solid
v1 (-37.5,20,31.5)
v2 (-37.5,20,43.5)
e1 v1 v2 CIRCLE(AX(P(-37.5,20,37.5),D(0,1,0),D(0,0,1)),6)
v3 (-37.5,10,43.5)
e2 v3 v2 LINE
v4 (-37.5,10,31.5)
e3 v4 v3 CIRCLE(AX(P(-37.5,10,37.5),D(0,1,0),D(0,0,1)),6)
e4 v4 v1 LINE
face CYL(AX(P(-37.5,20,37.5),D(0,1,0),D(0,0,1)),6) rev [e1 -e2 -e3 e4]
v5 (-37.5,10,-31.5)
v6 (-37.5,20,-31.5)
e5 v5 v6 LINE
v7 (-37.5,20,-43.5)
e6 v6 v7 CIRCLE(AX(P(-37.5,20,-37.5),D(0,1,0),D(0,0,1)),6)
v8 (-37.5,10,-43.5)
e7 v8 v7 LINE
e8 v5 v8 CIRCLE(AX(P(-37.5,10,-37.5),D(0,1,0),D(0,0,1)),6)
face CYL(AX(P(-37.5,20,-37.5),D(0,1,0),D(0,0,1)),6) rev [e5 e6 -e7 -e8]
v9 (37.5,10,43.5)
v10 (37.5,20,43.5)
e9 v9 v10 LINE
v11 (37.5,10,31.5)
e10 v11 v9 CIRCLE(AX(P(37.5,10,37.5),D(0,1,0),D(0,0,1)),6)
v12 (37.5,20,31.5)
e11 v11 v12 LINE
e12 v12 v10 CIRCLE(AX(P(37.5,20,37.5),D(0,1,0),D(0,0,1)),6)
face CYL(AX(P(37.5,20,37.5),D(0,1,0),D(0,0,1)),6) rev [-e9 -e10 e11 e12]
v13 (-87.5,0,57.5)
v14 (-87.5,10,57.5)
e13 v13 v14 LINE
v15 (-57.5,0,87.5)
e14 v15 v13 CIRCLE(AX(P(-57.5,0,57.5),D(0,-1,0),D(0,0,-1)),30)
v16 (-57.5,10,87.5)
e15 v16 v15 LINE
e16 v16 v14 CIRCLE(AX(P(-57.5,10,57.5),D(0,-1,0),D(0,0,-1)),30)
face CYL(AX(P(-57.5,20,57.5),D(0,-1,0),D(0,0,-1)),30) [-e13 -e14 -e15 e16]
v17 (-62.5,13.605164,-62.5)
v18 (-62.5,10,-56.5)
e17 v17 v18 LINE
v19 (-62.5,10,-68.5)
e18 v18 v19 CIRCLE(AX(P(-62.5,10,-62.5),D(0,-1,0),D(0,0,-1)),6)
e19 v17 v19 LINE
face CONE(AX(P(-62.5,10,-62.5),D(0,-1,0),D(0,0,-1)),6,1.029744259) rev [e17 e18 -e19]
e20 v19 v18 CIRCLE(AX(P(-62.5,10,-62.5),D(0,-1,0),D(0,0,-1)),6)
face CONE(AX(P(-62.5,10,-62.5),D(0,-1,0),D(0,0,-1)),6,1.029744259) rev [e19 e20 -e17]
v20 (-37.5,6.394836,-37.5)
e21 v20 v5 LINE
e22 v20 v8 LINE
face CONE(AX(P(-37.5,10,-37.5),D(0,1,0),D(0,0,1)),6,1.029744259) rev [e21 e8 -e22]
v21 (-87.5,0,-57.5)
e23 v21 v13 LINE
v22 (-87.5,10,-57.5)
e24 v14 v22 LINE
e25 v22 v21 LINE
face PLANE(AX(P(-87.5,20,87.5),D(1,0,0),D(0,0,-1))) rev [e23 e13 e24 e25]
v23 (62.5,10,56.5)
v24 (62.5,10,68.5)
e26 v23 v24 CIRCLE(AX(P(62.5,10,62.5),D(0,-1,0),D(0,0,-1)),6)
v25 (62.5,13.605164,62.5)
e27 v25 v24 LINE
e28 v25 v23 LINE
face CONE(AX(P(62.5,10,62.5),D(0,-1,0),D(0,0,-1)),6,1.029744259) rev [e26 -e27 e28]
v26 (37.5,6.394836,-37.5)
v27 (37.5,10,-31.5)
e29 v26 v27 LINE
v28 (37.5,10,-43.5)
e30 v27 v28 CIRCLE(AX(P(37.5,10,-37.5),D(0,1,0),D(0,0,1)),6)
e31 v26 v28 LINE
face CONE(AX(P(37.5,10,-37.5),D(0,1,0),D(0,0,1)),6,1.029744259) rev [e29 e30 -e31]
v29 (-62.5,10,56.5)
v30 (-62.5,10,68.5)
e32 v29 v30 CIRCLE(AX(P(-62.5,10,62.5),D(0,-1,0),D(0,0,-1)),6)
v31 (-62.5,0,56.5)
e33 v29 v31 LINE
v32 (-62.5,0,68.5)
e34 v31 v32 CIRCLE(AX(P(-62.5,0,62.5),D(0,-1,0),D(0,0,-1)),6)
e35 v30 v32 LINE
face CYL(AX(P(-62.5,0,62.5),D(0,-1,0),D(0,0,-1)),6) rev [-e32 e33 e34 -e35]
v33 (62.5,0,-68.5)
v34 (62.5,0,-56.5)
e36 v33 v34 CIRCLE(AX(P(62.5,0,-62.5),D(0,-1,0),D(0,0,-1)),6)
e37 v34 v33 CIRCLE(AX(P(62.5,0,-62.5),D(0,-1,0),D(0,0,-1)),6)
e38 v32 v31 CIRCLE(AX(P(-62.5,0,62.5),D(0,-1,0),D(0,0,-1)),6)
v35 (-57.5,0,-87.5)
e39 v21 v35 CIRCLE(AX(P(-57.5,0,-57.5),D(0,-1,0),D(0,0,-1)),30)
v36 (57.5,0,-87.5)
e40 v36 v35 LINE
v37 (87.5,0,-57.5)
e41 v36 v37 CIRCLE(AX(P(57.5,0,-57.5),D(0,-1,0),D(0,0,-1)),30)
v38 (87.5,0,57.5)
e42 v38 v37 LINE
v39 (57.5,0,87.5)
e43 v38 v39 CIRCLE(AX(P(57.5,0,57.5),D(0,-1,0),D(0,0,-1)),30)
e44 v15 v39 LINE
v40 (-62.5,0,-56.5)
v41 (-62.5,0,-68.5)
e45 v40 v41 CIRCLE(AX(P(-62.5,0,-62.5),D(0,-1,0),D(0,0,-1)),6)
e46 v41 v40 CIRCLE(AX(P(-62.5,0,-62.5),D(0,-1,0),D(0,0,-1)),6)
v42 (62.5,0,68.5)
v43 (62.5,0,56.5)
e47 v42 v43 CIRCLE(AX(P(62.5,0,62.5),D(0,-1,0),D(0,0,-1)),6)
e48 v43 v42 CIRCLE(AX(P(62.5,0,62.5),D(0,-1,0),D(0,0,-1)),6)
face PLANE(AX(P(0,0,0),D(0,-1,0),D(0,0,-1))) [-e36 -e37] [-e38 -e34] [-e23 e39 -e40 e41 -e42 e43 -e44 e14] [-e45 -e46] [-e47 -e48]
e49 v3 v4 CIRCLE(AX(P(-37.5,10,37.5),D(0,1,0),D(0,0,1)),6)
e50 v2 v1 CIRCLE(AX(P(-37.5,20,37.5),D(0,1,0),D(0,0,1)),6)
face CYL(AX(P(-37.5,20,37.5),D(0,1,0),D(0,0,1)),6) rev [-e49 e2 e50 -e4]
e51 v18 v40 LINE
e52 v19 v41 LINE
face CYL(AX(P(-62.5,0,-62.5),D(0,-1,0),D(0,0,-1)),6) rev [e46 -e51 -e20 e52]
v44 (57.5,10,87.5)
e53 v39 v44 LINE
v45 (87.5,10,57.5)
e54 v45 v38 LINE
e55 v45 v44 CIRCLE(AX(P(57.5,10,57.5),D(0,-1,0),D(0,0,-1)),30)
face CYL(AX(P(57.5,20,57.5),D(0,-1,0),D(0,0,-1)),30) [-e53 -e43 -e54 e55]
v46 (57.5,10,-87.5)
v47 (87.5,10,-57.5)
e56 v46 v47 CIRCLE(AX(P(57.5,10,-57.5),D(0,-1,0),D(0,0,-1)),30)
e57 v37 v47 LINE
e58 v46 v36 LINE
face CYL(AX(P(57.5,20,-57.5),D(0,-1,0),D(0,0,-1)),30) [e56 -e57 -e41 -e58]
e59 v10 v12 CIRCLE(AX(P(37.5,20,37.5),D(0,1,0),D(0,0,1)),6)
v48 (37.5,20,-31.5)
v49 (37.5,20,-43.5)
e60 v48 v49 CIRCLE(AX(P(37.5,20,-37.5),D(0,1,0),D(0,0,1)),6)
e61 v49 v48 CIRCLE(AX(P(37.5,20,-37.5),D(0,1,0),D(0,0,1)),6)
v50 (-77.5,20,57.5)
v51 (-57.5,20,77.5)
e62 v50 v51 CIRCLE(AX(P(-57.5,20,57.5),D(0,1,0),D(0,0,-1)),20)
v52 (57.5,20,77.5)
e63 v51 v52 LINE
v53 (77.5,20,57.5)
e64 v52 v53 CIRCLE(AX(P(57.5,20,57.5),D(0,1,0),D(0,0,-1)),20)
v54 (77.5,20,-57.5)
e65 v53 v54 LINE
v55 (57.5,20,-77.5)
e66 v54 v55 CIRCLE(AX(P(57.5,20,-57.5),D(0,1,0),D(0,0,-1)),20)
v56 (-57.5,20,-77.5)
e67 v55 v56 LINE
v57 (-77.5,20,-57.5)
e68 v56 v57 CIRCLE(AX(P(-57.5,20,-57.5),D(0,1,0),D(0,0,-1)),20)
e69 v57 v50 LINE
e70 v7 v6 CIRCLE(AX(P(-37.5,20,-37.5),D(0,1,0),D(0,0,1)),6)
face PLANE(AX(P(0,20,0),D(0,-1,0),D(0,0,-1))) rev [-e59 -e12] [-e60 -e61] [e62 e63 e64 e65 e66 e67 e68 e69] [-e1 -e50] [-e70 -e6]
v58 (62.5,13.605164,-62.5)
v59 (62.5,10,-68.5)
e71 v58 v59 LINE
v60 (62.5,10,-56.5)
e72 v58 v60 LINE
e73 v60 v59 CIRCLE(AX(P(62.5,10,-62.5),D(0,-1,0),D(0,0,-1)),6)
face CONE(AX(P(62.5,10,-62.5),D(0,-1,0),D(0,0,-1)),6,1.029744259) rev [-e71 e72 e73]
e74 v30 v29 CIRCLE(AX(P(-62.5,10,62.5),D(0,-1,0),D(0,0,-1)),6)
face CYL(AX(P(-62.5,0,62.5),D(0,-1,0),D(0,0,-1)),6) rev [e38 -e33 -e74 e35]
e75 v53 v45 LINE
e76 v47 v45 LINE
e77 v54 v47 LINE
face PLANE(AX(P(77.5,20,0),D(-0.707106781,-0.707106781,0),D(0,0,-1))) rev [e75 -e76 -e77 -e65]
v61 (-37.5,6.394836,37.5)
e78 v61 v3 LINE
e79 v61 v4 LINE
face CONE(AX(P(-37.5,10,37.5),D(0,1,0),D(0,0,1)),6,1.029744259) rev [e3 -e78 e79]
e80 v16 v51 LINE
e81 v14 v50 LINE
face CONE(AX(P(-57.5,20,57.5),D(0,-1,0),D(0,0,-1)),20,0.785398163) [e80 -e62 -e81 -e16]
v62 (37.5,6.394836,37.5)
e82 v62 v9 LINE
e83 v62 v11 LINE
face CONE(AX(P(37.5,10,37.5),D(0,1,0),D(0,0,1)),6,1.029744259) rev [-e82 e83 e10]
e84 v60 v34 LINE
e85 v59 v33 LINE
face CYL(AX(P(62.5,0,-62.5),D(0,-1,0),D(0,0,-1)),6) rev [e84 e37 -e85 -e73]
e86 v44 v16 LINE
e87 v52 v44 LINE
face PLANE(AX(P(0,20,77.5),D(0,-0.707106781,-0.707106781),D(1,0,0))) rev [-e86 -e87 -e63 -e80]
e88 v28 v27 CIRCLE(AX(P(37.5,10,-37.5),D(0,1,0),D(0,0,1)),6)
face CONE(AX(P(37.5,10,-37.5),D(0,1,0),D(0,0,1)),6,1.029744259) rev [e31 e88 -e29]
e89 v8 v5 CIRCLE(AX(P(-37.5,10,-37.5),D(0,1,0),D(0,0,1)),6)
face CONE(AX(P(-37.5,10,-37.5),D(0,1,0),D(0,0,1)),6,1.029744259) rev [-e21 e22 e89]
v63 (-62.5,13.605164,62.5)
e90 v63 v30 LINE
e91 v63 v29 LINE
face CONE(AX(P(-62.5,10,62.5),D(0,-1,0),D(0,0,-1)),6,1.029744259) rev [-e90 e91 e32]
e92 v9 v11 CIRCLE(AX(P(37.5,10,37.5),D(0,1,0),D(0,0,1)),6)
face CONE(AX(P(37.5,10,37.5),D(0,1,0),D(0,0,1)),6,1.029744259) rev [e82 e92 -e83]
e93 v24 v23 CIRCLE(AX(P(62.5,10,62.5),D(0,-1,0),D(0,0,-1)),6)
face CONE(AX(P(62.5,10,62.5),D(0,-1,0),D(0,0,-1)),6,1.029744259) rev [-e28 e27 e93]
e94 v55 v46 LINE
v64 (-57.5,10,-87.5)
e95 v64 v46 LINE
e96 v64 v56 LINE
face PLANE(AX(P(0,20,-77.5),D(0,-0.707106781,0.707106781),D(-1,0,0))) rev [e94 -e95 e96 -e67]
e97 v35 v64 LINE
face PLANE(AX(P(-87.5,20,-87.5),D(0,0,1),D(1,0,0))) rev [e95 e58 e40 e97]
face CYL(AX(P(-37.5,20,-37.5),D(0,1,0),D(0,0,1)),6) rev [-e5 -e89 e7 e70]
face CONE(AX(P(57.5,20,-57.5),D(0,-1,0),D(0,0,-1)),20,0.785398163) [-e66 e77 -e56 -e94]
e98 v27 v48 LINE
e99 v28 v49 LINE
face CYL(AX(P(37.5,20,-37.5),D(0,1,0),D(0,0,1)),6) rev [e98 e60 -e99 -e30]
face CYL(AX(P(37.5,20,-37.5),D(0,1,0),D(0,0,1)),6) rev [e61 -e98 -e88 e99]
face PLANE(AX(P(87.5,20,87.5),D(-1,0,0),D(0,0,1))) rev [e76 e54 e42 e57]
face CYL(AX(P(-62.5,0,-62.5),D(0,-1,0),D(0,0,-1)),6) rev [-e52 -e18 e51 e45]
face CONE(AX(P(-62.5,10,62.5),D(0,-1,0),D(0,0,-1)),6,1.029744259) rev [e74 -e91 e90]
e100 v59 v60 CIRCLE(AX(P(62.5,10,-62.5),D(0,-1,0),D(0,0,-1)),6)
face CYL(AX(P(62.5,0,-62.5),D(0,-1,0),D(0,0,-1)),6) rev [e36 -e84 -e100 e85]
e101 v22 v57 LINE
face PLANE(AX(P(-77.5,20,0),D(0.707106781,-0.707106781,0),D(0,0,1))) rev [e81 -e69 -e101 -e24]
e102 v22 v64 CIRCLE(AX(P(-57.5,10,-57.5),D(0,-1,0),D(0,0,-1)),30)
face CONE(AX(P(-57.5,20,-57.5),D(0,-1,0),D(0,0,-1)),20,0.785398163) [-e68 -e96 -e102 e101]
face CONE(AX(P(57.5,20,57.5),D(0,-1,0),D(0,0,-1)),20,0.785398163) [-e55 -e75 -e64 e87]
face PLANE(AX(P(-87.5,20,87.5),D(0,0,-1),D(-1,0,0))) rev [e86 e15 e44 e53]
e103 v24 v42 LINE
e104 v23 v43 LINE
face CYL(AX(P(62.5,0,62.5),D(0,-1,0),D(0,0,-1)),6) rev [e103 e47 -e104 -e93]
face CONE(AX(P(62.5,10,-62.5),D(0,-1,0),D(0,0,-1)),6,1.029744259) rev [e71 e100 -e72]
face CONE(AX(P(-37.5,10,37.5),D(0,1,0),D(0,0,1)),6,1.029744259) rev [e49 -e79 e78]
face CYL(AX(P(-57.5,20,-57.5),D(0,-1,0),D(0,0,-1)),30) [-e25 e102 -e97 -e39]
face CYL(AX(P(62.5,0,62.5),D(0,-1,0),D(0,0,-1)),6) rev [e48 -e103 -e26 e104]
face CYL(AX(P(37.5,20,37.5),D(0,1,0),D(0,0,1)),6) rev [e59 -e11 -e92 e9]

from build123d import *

# Parameters (mm, degrees)
BASE_PLATE_SKETCH_175X175_W = 175
BASE_PLATE_SKETCH_175X175_H = 175
BASE_PLATE_DEPTH            = 20
CORNER_FILLETS_R30_R        = 30
EDGE_CHAMFER_10X45_SIZE     = 10
DOWEL_HOLES_12_INNER_D      = 12
DOWEL_HOLES_12_INNER_DEPTH  = 10
DOWEL_HOLES_12_INNER_TIP    = 3.605163714
DOWEL_HOLES_12_OUTER_D      = 12
DOWEL_HOLES_12_OUTER_DEPTH  = 10
DOWEL_HOLES_12_OUTER_TIP    = 3.605163714


with BuildPart() as part:
    # Base Plate Sketch 175x175 → Base Plate (new body)
    with BuildSketch(Plane(origin=(0, 0, 0), x_dir=(1, 0, 0), z_dir=(0, 1, 0))):
        Rectangle(BASE_PLATE_SKETCH_175X175_W, BASE_PLATE_SKETCH_175X175_H)
    extrude(amount=BASE_PLATE_DEPTH)

    # Corner Fillets R30
    corner_fillets_r30_edges = [part.edges().sort_by_distance(p)[0] for p in [
        (87.5, 10, 87.5),
        (-87.5, 10, 87.5),
        (-87.5, 10, -87.5),
        (87.5, 10, -87.5),
    ]]
    fillet(corner_fillets_r30_edges, radius=CORNER_FILLETS_R30_R)

    # Edge Chamfer 10x45
    edge_chamfer_10x45_edges = [part.edges().sort_by_distance(p)[0] for p in [
        (-87.5, 20, 0),
        (0, 20, -87.5),
        (87.5, 20, 0),
        (0, 20, 87.5),
        (-78.713203436, 20, 78.713203436),
        (78.713203436, 20, 78.713203436),
        (78.713203436, 20, -78.713203436),
        (-78.713203436, 20, -78.713203436),
    ]]
    chamfer(edge_chamfer_10x45_edges, length=EDGE_CHAMFER_10X45_SIZE)

    # Dowel Holes Ø12 Inner
    with Locations(Plane(origin=(-37.5, 20, -37.5), x_dir=(0, 0, 1), z_dir=(0, 1, 0))):
        with Locations((0, 0), (0, 75), (75, 75), (75, 0)):
            Hole(DOWEL_HOLES_12_INNER_D / 2, depth=DOWEL_HOLES_12_INNER_DEPTH)
            with Locations((0, 0, -(DOWEL_HOLES_12_INNER_DEPTH + DOWEL_HOLES_12_INNER_TIP / 2))):  # 118° drill point
                Cone(0, DOWEL_HOLES_12_INNER_D / 2, DOWEL_HOLES_12_INNER_TIP, mode=Mode.SUBTRACT)

    # Dowel Holes Ø12 Outer
    with Locations(Plane(origin=(-62.5, 0, 62.5), x_dir=(0, 0, -1), z_dir=(0, -1, 0))):
        with Locations((0, 0), (0, 125), (125, 125), (125, 0)):
            Hole(DOWEL_HOLES_12_OUTER_D / 2, depth=DOWEL_HOLES_12_OUTER_DEPTH)
            with Locations((0, 0, -(DOWEL_HOLES_12_OUTER_DEPTH + DOWEL_HOLES_12_OUTER_TIP / 2))):  # 118° drill point
                Cone(0, DOWEL_HOLES_12_OUTER_D / 2, DOWEL_HOLES_12_OUTER_TIP, mode=Mode.SUBTRACT)


solid = part.part
